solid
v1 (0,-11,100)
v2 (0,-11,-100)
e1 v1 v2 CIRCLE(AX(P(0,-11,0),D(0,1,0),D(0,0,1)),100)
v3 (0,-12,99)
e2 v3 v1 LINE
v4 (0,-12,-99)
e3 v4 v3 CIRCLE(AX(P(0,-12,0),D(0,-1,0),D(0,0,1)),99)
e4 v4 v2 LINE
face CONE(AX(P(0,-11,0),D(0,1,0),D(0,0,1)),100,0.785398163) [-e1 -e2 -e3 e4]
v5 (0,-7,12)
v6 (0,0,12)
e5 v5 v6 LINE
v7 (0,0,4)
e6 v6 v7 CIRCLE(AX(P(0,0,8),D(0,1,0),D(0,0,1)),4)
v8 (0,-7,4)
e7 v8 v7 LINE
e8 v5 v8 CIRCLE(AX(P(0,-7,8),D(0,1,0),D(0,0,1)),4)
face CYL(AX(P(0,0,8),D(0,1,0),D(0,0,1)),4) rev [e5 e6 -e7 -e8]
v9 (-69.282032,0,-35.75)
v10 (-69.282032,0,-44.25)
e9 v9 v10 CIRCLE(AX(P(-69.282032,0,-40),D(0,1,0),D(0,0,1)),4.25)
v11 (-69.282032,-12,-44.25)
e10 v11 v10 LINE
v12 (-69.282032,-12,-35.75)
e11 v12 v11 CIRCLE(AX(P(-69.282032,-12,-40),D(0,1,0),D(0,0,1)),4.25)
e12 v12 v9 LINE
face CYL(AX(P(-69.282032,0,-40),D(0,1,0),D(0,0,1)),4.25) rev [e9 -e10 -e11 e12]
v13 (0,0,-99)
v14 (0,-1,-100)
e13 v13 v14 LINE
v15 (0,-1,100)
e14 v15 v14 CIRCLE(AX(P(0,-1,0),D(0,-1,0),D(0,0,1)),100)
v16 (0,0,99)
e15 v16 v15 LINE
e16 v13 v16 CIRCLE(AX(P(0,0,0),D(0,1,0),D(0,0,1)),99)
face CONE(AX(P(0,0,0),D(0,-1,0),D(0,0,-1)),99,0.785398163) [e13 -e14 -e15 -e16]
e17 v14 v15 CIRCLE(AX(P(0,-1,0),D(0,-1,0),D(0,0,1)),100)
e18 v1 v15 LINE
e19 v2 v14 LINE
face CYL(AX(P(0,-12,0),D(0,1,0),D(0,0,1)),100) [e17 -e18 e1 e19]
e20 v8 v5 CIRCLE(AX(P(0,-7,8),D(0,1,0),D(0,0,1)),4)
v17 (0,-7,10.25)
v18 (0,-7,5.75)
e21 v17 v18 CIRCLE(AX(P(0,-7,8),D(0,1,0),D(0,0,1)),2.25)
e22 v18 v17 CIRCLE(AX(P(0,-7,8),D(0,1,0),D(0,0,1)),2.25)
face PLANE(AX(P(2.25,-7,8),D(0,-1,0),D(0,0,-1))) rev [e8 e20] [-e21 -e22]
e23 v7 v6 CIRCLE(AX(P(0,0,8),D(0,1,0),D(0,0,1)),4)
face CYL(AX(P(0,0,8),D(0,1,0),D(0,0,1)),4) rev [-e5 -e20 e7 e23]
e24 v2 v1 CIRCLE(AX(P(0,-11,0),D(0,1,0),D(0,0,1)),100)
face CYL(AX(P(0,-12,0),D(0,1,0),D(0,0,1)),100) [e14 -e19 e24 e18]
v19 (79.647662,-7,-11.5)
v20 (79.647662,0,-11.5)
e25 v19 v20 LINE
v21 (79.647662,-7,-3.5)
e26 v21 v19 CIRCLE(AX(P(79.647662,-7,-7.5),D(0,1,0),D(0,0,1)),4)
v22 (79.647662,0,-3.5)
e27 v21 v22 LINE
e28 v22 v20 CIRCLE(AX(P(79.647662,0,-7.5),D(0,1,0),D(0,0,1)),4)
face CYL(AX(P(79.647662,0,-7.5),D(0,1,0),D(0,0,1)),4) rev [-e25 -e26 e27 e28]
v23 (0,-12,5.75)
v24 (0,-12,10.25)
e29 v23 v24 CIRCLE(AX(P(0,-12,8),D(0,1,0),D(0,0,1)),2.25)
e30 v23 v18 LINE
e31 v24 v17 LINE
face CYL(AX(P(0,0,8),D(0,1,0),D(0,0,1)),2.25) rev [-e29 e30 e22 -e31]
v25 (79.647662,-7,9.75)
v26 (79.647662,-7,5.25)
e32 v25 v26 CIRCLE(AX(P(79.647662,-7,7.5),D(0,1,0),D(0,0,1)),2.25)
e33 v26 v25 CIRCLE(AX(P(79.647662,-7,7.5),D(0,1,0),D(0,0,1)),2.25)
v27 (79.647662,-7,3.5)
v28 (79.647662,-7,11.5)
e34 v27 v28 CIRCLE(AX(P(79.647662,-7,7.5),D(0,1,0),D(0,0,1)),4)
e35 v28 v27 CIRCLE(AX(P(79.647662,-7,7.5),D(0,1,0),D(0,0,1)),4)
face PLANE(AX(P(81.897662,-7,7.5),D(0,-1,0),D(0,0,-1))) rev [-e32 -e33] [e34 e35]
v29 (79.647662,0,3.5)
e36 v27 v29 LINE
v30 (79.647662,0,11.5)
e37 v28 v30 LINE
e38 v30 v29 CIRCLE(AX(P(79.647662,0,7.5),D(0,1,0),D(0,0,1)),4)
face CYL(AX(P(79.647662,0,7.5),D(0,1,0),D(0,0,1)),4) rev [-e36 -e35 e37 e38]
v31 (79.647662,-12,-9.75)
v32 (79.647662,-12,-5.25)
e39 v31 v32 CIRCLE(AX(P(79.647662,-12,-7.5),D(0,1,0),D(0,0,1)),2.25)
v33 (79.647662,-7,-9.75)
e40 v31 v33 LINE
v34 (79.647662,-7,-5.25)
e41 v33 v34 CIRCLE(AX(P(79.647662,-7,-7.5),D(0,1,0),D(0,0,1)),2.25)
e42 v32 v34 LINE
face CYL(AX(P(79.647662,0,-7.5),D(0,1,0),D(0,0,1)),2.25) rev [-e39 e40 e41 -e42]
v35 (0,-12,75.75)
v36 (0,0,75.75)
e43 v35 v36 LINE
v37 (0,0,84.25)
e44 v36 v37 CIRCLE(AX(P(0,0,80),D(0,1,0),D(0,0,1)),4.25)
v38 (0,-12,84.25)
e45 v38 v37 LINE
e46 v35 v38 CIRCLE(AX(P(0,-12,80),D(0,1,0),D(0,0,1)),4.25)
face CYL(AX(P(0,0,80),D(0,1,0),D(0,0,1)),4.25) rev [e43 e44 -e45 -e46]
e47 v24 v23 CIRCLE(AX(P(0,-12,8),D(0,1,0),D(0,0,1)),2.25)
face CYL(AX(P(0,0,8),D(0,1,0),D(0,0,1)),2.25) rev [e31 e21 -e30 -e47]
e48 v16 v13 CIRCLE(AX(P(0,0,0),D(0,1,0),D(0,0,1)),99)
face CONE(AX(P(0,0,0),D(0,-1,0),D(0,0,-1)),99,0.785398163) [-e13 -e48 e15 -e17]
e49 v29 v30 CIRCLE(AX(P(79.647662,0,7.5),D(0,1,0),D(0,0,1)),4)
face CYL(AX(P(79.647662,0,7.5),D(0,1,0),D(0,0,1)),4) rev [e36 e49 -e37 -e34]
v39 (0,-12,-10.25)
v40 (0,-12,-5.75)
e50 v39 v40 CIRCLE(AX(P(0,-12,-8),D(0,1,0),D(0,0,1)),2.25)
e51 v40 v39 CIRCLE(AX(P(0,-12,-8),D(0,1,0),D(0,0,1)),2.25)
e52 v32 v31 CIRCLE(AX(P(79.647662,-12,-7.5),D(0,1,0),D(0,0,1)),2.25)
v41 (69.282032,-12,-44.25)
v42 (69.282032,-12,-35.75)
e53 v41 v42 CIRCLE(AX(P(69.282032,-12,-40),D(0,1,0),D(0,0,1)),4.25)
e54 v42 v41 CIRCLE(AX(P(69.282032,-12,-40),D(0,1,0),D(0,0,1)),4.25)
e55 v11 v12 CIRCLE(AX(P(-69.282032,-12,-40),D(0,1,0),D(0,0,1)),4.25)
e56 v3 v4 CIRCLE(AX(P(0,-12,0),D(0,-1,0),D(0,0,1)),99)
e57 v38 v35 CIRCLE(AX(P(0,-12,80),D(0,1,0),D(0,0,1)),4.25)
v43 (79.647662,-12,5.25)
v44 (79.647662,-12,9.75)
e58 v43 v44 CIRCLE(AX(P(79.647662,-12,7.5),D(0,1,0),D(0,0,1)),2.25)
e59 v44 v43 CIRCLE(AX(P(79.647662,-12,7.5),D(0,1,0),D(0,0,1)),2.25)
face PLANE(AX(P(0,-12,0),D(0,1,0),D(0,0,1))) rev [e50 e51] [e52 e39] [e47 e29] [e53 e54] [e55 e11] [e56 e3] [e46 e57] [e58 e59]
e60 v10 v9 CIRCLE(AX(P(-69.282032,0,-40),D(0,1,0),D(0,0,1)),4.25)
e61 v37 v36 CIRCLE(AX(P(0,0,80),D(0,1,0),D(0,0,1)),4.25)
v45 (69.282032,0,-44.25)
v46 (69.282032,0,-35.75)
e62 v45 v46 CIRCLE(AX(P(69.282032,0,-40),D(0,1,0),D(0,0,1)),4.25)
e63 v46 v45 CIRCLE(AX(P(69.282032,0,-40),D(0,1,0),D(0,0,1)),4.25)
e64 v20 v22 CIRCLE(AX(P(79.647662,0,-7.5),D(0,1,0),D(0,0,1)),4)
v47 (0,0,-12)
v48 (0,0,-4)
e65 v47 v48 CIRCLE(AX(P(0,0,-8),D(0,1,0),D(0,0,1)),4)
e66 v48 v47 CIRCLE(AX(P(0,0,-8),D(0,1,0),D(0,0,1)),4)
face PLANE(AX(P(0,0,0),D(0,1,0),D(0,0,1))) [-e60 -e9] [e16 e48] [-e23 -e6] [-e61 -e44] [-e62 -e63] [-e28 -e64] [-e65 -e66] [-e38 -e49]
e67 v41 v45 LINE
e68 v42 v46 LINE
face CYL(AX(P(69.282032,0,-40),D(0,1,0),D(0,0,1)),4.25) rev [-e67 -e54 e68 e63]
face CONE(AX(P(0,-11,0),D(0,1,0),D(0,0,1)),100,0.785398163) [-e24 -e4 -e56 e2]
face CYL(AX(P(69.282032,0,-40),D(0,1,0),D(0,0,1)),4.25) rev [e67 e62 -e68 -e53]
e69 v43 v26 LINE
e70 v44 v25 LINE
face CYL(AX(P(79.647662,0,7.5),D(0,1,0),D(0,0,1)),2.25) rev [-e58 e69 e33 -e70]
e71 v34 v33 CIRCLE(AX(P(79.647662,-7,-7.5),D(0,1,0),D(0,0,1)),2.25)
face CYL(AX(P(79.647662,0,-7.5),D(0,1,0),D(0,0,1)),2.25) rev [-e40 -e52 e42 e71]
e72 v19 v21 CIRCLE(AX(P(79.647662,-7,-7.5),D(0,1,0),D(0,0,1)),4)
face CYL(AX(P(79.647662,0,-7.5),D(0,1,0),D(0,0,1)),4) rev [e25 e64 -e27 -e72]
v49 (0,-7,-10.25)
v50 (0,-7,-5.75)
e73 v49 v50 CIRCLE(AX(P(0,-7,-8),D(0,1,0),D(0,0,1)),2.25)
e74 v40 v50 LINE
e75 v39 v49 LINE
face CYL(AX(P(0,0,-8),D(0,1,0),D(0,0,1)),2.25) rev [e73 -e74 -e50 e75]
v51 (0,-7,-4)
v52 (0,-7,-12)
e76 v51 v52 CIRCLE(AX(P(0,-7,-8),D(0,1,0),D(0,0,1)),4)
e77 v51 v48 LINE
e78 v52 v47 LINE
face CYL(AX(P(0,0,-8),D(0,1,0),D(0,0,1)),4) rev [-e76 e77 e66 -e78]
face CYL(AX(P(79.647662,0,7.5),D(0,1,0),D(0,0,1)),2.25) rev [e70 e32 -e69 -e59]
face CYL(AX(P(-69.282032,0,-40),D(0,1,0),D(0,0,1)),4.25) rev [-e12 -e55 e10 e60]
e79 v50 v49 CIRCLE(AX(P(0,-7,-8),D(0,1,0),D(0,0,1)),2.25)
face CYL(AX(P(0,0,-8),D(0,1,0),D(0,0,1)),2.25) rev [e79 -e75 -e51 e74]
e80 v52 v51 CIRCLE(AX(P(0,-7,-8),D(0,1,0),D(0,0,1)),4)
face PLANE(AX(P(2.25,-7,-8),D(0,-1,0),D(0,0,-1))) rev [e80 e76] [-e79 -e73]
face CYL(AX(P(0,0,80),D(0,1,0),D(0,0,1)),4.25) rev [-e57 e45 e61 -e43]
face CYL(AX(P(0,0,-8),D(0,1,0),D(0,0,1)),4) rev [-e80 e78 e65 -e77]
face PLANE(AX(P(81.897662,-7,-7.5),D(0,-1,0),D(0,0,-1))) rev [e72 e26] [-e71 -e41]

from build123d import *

# Parameters (mm, degrees)
SKETCH2_R                               = 100
BOSS_EXTRUDE1_DEPTH                     = 12
M10_TAPPED_HOLE1_D                      = 8.5
M10_TAPPED_HOLE1_DEPTH                  = 24.5
M10_TAPPED_HOLE1_TIP                    = 2.553657631
CBORE_FOR_M4_HEX_HEAD_BOLT1_D           = 4.5
CBORE_FOR_M4_HEX_HEAD_BOLT1_DEPTH       = 24.5
CBORE_FOR_M4_HEX_HEAD_BOLT1_CBORE_D     = 8
CBORE_FOR_M4_HEX_HEAD_BOLT1_CBORE_DEPTH = 7
CBORE_FOR_M4_HEX_HEAD_BOLT1_TIP         = 1.351936393
CHAMFER1_SIZE                           = 1


with BuildPart() as part:
    # Sketch2 → Boss-Extrude1 (new body)
    with BuildSketch(Plane(origin=(0, 0, 0), x_dir=(1, 0, 0), z_dir=(0, 1, 0))):
        with Locations(Location((0, 0, 0), (0, 0, 270))):
            Circle(SKETCH2_R)
    extrude(amount=-BOSS_EXTRUDE1_DEPTH)

    # M10 Tapped Hole1
    with Locations(Plane(origin=(-69.282032303, 0, -40), x_dir=(0, 0, 1), z_dir=(0, 1, 0))):
        with Locations((0, 0), (0, 138.564064606), (120, 69.282032303)):
            Hole(M10_TAPPED_HOLE1_D / 2, depth=M10_TAPPED_HOLE1_DEPTH)
            with Locations((0, 0, -(M10_TAPPED_HOLE1_DEPTH + M10_TAPPED_HOLE1_TIP / 2))):  # 118° drill point
                Cone(0, M10_TAPPED_HOLE1_D / 2, M10_TAPPED_HOLE1_TIP, mode=Mode.SUBTRACT)

    # CBORE for M4 Hex Head Bolt1
    with Locations(Plane(origin=(79.64766161, 0, -7.5), x_dir=(0, 0, 1), z_dir=(0, 1, 0))):
        with Locations((0, 0), (15, 0), (15.5, -79.64766161), (-0.5, -79.64766161)):
            CounterBoreHole(CBORE_FOR_M4_HEX_HEAD_BOLT1_D / 2, CBORE_FOR_M4_HEX_HEAD_BOLT1_CBORE_D / 2, CBORE_FOR_M4_HEX_HEAD_BOLT1_CBORE_DEPTH, depth=CBORE_FOR_M4_HEX_HEAD_BOLT1_DEPTH)
            with Locations((0, 0, -(CBORE_FOR_M4_HEX_HEAD_BOLT1_DEPTH + CBORE_FOR_M4_HEX_HEAD_BOLT1_TIP / 2))):  # 118° drill point
                Cone(0, CBORE_FOR_M4_HEX_HEAD_BOLT1_D / 2, CBORE_FOR_M4_HEX_HEAD_BOLT1_TIP, mode=Mode.SUBTRACT)

    # Chamfer1
    chamfer1_edges = [part.edges().sort_by_distance(p)[0] for p in [
        (0, 0, -100),
        (0, -12, -100),
    ]]
    chamfer(chamfer1_edges, length=CHAMFER1_SIZE)


solid = part.part
